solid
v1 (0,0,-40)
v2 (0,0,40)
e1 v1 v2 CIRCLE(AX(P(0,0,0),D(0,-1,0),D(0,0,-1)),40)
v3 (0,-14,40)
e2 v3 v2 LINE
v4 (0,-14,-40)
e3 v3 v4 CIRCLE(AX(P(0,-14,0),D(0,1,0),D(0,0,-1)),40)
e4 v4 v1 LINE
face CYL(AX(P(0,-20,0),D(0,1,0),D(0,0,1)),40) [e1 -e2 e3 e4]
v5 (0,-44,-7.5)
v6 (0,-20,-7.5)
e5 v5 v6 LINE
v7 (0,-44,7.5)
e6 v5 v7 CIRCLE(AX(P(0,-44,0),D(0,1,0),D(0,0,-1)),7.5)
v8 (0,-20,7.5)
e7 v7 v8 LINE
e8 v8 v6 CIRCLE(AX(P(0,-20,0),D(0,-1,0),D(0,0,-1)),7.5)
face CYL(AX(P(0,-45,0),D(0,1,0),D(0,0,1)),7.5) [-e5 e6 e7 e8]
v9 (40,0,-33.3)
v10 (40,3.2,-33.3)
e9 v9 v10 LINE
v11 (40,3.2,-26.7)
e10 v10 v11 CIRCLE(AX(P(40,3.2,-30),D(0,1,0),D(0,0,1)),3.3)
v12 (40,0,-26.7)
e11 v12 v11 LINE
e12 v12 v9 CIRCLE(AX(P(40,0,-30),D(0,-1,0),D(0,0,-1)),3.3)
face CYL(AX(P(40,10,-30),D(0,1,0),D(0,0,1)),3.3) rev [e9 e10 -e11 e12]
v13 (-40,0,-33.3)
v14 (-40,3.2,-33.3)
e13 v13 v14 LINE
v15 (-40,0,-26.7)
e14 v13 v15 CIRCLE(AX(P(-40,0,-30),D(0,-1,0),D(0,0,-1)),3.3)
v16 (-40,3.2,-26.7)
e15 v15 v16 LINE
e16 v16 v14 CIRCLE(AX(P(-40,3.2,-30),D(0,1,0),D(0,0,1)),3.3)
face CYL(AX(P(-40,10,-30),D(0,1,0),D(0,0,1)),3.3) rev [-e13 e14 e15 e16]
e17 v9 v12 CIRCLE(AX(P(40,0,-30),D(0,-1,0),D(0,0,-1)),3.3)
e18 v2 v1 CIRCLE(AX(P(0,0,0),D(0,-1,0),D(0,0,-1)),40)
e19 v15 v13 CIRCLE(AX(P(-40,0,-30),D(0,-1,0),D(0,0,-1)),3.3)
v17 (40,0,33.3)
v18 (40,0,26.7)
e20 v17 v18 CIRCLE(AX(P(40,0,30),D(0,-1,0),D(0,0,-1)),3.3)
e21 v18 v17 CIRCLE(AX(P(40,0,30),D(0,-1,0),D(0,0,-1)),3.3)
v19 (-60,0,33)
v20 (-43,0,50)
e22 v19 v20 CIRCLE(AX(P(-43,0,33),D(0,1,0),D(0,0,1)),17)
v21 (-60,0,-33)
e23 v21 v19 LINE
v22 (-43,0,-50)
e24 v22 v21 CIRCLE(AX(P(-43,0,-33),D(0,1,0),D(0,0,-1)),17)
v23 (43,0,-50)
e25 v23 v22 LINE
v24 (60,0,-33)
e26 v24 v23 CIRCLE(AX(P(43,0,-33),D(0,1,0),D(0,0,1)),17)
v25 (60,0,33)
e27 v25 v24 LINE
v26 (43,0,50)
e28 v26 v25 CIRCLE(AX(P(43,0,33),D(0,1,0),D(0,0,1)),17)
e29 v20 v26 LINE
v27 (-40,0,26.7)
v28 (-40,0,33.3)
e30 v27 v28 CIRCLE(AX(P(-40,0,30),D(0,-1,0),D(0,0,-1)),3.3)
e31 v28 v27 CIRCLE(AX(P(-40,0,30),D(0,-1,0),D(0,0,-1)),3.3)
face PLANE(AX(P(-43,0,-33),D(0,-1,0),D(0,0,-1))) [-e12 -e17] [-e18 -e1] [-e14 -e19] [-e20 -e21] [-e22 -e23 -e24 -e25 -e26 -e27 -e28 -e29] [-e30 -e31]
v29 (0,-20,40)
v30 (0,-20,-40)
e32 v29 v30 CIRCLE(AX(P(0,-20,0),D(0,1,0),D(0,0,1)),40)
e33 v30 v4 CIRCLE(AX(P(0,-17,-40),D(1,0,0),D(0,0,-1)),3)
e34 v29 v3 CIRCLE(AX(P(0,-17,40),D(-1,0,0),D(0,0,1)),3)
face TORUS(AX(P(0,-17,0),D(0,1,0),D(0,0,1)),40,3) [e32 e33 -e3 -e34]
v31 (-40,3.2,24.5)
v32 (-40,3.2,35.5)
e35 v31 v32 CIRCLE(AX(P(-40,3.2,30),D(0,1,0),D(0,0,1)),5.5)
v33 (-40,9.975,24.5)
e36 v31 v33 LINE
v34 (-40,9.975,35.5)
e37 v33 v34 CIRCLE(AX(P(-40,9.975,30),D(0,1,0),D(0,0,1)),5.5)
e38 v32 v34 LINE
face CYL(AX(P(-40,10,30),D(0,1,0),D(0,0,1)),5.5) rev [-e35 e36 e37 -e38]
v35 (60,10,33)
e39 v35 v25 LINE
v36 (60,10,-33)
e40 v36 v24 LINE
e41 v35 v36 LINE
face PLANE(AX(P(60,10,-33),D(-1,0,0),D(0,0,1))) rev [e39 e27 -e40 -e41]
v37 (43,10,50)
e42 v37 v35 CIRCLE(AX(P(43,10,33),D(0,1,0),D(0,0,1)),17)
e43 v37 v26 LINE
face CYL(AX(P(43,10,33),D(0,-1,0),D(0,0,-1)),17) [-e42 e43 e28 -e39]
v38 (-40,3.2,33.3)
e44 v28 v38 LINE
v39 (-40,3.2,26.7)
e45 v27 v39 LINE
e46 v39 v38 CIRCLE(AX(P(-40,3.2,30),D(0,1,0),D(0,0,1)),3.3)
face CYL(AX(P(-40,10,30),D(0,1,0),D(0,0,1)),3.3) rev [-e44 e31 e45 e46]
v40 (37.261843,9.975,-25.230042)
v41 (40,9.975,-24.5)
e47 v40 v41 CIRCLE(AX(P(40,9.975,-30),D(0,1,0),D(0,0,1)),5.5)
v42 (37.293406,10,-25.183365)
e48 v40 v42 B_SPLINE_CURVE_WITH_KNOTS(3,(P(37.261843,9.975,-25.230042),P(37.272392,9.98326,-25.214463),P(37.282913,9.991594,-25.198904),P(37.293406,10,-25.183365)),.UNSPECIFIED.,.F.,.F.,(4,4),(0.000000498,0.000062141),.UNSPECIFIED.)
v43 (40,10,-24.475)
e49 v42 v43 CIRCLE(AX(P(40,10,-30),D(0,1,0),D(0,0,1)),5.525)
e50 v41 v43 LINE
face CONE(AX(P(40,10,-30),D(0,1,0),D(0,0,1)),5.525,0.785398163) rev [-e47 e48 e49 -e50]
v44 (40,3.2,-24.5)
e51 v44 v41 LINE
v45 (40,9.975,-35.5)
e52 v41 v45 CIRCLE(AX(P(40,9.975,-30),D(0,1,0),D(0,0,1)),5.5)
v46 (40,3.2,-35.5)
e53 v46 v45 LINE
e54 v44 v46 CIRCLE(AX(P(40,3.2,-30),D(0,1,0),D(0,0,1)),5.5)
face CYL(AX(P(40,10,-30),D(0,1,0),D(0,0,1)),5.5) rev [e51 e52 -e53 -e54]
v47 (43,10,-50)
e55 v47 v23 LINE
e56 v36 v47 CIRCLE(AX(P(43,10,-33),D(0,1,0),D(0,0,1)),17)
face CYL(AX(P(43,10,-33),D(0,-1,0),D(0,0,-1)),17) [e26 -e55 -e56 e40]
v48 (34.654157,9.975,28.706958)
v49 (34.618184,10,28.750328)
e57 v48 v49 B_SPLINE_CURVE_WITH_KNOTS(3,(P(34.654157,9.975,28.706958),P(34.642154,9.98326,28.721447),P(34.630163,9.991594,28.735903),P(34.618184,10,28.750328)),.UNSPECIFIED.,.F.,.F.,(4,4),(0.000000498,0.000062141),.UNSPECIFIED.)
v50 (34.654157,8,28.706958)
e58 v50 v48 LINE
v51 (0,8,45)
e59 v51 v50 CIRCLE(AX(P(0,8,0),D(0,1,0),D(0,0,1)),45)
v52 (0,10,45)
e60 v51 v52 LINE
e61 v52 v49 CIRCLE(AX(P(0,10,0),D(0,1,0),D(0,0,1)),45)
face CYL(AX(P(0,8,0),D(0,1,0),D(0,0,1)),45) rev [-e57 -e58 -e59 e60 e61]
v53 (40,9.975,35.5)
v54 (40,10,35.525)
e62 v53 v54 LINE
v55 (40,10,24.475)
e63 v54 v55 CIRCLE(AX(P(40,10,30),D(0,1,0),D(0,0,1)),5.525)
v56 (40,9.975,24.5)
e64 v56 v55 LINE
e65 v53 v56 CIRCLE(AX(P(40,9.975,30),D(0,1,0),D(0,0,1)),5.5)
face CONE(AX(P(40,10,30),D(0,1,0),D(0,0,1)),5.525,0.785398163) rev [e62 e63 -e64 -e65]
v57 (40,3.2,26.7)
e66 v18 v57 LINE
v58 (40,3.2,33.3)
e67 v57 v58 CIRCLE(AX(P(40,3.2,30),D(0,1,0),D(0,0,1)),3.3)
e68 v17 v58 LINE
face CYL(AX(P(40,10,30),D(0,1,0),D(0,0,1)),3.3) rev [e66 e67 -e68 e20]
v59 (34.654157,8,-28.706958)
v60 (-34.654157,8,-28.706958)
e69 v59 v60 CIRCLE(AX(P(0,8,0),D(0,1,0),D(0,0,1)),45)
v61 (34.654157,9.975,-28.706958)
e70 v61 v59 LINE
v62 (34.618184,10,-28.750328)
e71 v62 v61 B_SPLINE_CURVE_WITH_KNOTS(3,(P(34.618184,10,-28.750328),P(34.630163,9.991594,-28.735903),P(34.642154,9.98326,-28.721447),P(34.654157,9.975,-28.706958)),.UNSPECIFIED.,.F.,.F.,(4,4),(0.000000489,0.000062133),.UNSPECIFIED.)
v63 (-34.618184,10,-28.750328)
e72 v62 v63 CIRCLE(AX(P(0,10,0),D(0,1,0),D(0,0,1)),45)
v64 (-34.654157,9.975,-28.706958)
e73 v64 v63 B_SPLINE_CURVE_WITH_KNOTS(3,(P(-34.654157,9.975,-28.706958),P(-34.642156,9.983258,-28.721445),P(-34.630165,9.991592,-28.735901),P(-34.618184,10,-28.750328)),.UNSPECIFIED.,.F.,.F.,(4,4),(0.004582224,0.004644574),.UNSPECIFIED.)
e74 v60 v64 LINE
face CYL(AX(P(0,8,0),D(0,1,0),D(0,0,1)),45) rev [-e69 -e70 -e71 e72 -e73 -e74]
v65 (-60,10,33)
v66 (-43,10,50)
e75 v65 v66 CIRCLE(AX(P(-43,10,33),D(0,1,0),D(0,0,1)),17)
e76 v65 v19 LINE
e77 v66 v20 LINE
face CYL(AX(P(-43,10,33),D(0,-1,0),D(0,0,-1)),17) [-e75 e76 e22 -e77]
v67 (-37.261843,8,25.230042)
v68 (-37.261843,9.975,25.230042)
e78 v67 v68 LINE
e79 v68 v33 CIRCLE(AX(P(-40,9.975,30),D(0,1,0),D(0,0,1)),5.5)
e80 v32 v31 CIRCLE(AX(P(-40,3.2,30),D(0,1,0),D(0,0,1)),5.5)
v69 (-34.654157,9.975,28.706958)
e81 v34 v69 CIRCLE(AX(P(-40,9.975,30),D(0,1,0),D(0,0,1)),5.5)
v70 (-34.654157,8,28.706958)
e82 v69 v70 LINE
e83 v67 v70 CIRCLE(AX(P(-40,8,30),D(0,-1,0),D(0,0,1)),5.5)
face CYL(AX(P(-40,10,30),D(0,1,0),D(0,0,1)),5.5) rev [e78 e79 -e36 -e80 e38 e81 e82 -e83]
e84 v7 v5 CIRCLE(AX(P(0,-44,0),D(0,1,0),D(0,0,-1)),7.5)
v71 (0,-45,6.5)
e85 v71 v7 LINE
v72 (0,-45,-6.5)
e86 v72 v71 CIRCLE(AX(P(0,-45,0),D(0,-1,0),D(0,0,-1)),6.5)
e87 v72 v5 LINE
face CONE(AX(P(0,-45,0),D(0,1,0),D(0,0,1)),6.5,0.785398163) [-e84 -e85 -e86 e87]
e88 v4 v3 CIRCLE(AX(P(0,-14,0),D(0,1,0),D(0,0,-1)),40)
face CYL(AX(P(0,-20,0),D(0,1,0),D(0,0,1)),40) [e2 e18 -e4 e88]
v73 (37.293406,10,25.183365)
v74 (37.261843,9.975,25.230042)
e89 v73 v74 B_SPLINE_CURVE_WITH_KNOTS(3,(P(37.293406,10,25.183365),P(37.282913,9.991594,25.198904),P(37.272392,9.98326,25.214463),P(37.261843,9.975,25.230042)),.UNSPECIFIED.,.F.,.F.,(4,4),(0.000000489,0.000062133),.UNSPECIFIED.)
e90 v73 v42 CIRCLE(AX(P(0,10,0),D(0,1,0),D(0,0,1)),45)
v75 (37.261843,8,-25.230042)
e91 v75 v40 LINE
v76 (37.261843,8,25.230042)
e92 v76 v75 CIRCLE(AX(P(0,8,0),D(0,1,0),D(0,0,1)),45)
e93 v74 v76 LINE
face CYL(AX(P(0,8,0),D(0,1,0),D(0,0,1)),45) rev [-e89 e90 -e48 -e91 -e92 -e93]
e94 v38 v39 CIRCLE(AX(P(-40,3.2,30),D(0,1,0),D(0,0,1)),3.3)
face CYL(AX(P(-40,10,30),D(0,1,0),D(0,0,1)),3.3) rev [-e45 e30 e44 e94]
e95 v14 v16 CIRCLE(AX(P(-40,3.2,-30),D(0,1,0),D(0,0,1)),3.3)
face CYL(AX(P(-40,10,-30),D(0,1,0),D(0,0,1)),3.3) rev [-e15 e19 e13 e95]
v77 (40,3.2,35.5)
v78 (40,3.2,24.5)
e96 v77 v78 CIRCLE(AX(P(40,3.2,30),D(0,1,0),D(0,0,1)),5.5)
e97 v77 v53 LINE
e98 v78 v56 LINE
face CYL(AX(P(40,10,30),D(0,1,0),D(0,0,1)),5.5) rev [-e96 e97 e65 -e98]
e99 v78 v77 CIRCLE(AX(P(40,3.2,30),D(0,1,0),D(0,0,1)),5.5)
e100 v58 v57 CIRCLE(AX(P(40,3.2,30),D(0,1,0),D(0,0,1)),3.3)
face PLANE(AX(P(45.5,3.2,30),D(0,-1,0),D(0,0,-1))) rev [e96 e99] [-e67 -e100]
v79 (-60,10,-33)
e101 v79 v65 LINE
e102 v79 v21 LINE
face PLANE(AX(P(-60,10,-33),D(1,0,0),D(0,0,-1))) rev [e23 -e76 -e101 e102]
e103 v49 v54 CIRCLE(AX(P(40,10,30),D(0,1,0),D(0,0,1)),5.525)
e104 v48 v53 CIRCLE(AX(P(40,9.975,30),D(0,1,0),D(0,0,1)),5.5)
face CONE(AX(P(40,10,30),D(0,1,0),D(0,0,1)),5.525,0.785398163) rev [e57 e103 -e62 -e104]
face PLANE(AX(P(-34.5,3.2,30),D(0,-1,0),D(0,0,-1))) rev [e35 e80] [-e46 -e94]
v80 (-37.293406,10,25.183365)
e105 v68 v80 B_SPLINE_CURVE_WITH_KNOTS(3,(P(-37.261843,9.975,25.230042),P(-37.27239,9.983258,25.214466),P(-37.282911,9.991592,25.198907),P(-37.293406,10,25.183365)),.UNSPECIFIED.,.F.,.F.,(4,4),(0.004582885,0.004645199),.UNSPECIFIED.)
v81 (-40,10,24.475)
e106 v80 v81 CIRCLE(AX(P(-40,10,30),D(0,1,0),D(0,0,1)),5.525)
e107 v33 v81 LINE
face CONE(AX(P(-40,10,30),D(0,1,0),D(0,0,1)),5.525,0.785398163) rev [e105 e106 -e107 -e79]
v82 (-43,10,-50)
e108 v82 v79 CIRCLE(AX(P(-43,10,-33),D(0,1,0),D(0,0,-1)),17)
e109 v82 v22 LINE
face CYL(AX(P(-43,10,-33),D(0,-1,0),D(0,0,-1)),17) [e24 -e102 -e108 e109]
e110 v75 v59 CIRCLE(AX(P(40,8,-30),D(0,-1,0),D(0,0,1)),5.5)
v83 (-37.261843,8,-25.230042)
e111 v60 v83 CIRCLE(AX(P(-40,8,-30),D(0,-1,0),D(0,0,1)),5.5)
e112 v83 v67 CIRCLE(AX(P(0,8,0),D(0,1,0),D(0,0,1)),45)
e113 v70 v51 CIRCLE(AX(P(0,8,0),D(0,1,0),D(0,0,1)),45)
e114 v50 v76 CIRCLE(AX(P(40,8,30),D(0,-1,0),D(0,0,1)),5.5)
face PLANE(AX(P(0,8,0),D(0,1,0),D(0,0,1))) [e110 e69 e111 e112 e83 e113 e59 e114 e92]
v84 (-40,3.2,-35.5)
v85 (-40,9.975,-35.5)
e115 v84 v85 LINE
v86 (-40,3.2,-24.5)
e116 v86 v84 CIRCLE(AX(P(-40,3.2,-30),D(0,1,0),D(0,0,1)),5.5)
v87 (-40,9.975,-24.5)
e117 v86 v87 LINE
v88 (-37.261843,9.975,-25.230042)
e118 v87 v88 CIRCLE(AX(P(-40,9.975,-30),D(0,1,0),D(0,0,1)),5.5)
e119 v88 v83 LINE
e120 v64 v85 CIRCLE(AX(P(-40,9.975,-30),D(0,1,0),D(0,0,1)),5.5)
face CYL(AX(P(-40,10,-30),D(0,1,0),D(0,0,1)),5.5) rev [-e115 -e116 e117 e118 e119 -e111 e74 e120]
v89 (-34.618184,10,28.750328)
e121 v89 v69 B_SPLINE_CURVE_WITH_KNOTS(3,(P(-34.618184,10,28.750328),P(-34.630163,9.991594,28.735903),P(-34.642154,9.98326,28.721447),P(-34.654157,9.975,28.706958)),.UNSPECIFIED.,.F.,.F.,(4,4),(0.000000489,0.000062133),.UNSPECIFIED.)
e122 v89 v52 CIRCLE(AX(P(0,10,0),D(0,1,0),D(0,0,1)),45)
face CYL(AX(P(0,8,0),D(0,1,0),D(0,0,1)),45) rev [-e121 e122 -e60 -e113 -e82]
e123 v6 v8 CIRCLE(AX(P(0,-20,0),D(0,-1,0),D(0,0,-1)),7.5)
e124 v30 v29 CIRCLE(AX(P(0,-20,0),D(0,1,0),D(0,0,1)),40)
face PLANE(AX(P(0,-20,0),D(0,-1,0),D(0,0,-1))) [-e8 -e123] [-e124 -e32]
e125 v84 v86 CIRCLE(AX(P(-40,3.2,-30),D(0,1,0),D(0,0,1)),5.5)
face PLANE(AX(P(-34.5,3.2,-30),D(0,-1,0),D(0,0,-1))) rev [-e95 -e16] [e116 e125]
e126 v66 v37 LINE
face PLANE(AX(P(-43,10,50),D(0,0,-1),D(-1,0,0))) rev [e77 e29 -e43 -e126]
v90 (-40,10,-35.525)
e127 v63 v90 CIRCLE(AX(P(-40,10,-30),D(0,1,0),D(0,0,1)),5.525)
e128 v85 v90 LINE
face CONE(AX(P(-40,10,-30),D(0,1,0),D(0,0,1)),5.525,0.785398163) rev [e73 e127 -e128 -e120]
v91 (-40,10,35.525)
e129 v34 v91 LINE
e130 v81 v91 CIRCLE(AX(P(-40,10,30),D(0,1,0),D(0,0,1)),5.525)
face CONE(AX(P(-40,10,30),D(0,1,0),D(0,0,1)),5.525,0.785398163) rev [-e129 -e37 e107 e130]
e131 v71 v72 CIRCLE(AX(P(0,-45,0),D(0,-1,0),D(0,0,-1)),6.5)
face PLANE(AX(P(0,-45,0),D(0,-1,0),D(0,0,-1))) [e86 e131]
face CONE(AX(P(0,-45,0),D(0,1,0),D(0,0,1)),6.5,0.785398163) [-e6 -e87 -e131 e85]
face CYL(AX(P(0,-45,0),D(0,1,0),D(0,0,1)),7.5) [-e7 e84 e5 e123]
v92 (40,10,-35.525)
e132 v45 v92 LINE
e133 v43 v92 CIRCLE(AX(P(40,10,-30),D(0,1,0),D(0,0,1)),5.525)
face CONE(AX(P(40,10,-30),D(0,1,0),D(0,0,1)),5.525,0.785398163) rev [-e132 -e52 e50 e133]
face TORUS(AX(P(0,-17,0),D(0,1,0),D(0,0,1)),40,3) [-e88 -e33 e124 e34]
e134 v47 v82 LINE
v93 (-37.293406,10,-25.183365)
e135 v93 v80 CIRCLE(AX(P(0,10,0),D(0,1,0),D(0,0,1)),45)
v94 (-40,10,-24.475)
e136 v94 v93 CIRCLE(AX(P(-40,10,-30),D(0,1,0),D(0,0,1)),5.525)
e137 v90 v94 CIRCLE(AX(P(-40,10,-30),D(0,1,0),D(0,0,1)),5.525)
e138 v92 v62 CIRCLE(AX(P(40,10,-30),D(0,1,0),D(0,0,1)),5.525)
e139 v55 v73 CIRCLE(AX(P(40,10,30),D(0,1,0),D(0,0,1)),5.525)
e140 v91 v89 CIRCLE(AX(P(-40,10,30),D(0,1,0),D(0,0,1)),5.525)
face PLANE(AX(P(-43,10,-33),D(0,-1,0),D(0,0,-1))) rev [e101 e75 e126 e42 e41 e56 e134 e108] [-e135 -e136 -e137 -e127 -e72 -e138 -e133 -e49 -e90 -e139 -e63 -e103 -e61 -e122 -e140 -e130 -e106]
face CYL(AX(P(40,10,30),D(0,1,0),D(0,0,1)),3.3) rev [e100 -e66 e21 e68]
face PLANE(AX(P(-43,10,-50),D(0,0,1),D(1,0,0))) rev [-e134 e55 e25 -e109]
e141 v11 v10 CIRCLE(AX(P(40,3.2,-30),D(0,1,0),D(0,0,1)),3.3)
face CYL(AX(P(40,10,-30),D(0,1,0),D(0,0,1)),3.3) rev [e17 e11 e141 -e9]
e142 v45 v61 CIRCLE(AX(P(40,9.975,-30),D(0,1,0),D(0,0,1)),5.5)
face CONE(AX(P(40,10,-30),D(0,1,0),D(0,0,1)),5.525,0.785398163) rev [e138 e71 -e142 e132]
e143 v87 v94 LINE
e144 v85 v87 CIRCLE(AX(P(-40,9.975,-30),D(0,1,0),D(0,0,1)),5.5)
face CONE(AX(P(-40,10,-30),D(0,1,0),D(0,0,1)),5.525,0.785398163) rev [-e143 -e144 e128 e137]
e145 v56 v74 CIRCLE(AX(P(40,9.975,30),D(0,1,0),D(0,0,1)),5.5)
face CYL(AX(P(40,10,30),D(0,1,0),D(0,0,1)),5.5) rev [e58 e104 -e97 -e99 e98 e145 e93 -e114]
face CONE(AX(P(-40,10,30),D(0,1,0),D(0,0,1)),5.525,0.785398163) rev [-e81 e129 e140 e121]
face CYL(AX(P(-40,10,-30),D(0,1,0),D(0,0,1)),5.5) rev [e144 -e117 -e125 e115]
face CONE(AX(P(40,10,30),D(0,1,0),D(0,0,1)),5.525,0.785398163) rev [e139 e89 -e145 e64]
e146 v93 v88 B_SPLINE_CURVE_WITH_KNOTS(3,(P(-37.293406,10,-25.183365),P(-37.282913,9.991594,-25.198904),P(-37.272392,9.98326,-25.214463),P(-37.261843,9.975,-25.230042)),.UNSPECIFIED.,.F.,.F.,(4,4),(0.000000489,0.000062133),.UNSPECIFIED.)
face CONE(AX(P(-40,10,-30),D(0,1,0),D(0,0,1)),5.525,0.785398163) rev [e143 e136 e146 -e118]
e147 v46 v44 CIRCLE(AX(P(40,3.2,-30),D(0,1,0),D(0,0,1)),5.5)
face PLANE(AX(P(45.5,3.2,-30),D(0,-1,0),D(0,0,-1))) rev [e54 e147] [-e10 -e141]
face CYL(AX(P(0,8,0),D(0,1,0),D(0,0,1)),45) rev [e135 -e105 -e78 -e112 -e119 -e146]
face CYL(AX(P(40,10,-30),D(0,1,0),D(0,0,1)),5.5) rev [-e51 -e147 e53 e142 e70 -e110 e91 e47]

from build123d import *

# Parameters (mm, degrees)
BOSS_EXTRUDE1_DEPTH                          = 10
SKETCH2_R                                    = 40
BOSS_EXTRUDE2_DEPTH                          = 20
SKETCH3_R                                    = 3
CBORE_FOR_M6_HEXAGON_SOCKET_HEAD_CAP_2_COUNT = 2
CBORE_FOR_M6_HEXAGON_SOCKET_HEAD_CAP_2_PITCH = 80
CBORE_FOR_M6_HEXAGON_SOCKET_HEAD_CAP_3_COUNT = 2
CBORE_FOR_M6_HEXAGON_SOCKET_HEAD_CAP_3_PITCH = 100
CBORE_FOR_M6_HEXAGON_SOCKET_HEAD_CAP_4_COUNT = 2
CBORE_FOR_M6_HEXAGON_SOCKET_HEAD_CAP_4_PITCH = 60
SKETCH4_R                                    = 7.5
BOSS_EXTRUDE3_DEPTH                          = 25
CHAMFER1_SIZE                                = 1
SKETCH5_R                                    = 45
CUT_EXTRUDE1_DEPTH                           = 2


with BuildPart() as part:
    # Sketch1 → Boss-Extrude1 (new body)
    with BuildSketch(Plane(origin=(0, 0, 0), x_dir=(1, 0, 0), z_dir=(0, 1, 0))):
        with BuildLine():
            Line((-43, 50), (43, 50))
            ThreePointArc((43, 50), (55.02081528, 45.02081528), (60, 33))
            Line((60, 33), (60, -33))
            ThreePointArc((60, -33), (55.02081528, -45.02081528), (43, -50))
            Line((43, -50), (-43, -50))
            ThreePointArc((-43, -50), (-55.02081528, -45.02081528), (-60, -33))
            Line((-60, -33), (-60, 33))
            ThreePointArc((-60, 33), (-55.02081528, 45.02081528), (-43, 50))
        make_face()
    extrude(amount=BOSS_EXTRUDE1_DEPTH)

    # Sketch2 → Boss-Extrude2 (add)
    with BuildSketch(Plane.XZ):
        with Locations(Location((0, 0, 0), (0, 0, 270))):
            Circle(SKETCH2_R)
    extrude(amount=BOSS_EXTRUDE2_DEPTH)

    # Sketch3 → Revolve1 (revolve)
    with BuildSketch(Plane(origin=(0, 0, 0), x_dir=(0, 0, -1), z_dir=(1, 0, 0)), mode=Mode.PRIVATE) as revolve1_sk:
        with Locations((-40, -17)):
            Circle(SKETCH3_R)
    revolve(revolve1_sk.sketch.rotate(Axis((0, 22.515244343, 0), (0, -1, 0)), 180), axis=Axis((0, 22.515244343, 0), (0, -1, 0)))

    # Sketch9 → CBORE for M6 Hexagon socket head cap screws1 (revolve, cut)
    with BuildSketch(Plane(origin=(-40, 10, -30), x_dir=(0, 0, 1), z_dir=(1, 0, 0))):
        Polygon((0, 0), (0, 30), (3.3, 30), (3.3, 6.8), (5.5, 6.8), (5.5, 0.025), (5.525, 0), align=None)
    cbore_for_m6_hexagon_socket_head_cap_scr = revolve(axis=Axis((-40, 16.35, -30), (0, -1, 0)), mode=Mode.SUBTRACT)

    # CBORE for M6 Hexagon socket head cap 2: CBORE for M6 Hexagon socket head cap screws1 ×2
    with Locations(*[(i * CBORE_FOR_M6_HEXAGON_SOCKET_HEAD_CAP_2_PITCH, 0, 0) for i in range(1, CBORE_FOR_M6_HEXAGON_SOCKET_HEAD_CAP_2_COUNT)]):
        add(cbore_for_m6_hexagon_socket_head_cap_scr, mode=Mode.SUBTRACT)

    # CBORE for M6 Hexagon socket head cap 3: CBORE for M6 Hexagon socket head cap screws1 ×2
    with Locations(*[Vector(0.7999999999999999, 0, 0.6000000000000001) * (i * CBORE_FOR_M6_HEXAGON_SOCKET_HEAD_CAP_3_PITCH) for i in range(1, CBORE_FOR_M6_HEXAGON_SOCKET_HEAD_CAP_3_COUNT)]):
        add(cbore_for_m6_hexagon_socket_head_cap_scr, mode=Mode.SUBTRACT)

    # CBORE for M6 Hexagon socket head cap 4: CBORE for M6 Hexagon socket head cap screws1 ×2
    with Locations(*[(0, 0, i * CBORE_FOR_M6_HEXAGON_SOCKET_HEAD_CAP_4_PITCH) for i in range(1, CBORE_FOR_M6_HEXAGON_SOCKET_HEAD_CAP_4_COUNT)]):
        add(cbore_for_m6_hexagon_socket_head_cap_scr, mode=Mode.SUBTRACT)

    # Sketch4 → Boss-Extrude3 (add)
    with BuildSketch(Plane.XZ.offset(20)):
        with Locations(Location((0, 0, 0), (0, 0, 270))):
            Circle(SKETCH4_R)
    extrude(amount=BOSS_EXTRUDE3_DEPTH)

    # Chamfer1
    chamfer1_edges = [part.edges().sort_by_distance(p)[0] for p in [
        (0, -45, 7.5),
    ]]
    chamfer(chamfer1_edges, length=CHAMFER1_SIZE)

    # Sketch5 → Cut-Extrude1 (cut)
    with BuildSketch(Plane(origin=(0, 10, 0), x_dir=(1, 0, 0), z_dir=(0, 1, 0))):
        Circle(SKETCH5_R)
    extrude(amount=-CUT_EXTRUDE1_DEPTH, mode=Mode.SUBTRACT)


solid = part.part
